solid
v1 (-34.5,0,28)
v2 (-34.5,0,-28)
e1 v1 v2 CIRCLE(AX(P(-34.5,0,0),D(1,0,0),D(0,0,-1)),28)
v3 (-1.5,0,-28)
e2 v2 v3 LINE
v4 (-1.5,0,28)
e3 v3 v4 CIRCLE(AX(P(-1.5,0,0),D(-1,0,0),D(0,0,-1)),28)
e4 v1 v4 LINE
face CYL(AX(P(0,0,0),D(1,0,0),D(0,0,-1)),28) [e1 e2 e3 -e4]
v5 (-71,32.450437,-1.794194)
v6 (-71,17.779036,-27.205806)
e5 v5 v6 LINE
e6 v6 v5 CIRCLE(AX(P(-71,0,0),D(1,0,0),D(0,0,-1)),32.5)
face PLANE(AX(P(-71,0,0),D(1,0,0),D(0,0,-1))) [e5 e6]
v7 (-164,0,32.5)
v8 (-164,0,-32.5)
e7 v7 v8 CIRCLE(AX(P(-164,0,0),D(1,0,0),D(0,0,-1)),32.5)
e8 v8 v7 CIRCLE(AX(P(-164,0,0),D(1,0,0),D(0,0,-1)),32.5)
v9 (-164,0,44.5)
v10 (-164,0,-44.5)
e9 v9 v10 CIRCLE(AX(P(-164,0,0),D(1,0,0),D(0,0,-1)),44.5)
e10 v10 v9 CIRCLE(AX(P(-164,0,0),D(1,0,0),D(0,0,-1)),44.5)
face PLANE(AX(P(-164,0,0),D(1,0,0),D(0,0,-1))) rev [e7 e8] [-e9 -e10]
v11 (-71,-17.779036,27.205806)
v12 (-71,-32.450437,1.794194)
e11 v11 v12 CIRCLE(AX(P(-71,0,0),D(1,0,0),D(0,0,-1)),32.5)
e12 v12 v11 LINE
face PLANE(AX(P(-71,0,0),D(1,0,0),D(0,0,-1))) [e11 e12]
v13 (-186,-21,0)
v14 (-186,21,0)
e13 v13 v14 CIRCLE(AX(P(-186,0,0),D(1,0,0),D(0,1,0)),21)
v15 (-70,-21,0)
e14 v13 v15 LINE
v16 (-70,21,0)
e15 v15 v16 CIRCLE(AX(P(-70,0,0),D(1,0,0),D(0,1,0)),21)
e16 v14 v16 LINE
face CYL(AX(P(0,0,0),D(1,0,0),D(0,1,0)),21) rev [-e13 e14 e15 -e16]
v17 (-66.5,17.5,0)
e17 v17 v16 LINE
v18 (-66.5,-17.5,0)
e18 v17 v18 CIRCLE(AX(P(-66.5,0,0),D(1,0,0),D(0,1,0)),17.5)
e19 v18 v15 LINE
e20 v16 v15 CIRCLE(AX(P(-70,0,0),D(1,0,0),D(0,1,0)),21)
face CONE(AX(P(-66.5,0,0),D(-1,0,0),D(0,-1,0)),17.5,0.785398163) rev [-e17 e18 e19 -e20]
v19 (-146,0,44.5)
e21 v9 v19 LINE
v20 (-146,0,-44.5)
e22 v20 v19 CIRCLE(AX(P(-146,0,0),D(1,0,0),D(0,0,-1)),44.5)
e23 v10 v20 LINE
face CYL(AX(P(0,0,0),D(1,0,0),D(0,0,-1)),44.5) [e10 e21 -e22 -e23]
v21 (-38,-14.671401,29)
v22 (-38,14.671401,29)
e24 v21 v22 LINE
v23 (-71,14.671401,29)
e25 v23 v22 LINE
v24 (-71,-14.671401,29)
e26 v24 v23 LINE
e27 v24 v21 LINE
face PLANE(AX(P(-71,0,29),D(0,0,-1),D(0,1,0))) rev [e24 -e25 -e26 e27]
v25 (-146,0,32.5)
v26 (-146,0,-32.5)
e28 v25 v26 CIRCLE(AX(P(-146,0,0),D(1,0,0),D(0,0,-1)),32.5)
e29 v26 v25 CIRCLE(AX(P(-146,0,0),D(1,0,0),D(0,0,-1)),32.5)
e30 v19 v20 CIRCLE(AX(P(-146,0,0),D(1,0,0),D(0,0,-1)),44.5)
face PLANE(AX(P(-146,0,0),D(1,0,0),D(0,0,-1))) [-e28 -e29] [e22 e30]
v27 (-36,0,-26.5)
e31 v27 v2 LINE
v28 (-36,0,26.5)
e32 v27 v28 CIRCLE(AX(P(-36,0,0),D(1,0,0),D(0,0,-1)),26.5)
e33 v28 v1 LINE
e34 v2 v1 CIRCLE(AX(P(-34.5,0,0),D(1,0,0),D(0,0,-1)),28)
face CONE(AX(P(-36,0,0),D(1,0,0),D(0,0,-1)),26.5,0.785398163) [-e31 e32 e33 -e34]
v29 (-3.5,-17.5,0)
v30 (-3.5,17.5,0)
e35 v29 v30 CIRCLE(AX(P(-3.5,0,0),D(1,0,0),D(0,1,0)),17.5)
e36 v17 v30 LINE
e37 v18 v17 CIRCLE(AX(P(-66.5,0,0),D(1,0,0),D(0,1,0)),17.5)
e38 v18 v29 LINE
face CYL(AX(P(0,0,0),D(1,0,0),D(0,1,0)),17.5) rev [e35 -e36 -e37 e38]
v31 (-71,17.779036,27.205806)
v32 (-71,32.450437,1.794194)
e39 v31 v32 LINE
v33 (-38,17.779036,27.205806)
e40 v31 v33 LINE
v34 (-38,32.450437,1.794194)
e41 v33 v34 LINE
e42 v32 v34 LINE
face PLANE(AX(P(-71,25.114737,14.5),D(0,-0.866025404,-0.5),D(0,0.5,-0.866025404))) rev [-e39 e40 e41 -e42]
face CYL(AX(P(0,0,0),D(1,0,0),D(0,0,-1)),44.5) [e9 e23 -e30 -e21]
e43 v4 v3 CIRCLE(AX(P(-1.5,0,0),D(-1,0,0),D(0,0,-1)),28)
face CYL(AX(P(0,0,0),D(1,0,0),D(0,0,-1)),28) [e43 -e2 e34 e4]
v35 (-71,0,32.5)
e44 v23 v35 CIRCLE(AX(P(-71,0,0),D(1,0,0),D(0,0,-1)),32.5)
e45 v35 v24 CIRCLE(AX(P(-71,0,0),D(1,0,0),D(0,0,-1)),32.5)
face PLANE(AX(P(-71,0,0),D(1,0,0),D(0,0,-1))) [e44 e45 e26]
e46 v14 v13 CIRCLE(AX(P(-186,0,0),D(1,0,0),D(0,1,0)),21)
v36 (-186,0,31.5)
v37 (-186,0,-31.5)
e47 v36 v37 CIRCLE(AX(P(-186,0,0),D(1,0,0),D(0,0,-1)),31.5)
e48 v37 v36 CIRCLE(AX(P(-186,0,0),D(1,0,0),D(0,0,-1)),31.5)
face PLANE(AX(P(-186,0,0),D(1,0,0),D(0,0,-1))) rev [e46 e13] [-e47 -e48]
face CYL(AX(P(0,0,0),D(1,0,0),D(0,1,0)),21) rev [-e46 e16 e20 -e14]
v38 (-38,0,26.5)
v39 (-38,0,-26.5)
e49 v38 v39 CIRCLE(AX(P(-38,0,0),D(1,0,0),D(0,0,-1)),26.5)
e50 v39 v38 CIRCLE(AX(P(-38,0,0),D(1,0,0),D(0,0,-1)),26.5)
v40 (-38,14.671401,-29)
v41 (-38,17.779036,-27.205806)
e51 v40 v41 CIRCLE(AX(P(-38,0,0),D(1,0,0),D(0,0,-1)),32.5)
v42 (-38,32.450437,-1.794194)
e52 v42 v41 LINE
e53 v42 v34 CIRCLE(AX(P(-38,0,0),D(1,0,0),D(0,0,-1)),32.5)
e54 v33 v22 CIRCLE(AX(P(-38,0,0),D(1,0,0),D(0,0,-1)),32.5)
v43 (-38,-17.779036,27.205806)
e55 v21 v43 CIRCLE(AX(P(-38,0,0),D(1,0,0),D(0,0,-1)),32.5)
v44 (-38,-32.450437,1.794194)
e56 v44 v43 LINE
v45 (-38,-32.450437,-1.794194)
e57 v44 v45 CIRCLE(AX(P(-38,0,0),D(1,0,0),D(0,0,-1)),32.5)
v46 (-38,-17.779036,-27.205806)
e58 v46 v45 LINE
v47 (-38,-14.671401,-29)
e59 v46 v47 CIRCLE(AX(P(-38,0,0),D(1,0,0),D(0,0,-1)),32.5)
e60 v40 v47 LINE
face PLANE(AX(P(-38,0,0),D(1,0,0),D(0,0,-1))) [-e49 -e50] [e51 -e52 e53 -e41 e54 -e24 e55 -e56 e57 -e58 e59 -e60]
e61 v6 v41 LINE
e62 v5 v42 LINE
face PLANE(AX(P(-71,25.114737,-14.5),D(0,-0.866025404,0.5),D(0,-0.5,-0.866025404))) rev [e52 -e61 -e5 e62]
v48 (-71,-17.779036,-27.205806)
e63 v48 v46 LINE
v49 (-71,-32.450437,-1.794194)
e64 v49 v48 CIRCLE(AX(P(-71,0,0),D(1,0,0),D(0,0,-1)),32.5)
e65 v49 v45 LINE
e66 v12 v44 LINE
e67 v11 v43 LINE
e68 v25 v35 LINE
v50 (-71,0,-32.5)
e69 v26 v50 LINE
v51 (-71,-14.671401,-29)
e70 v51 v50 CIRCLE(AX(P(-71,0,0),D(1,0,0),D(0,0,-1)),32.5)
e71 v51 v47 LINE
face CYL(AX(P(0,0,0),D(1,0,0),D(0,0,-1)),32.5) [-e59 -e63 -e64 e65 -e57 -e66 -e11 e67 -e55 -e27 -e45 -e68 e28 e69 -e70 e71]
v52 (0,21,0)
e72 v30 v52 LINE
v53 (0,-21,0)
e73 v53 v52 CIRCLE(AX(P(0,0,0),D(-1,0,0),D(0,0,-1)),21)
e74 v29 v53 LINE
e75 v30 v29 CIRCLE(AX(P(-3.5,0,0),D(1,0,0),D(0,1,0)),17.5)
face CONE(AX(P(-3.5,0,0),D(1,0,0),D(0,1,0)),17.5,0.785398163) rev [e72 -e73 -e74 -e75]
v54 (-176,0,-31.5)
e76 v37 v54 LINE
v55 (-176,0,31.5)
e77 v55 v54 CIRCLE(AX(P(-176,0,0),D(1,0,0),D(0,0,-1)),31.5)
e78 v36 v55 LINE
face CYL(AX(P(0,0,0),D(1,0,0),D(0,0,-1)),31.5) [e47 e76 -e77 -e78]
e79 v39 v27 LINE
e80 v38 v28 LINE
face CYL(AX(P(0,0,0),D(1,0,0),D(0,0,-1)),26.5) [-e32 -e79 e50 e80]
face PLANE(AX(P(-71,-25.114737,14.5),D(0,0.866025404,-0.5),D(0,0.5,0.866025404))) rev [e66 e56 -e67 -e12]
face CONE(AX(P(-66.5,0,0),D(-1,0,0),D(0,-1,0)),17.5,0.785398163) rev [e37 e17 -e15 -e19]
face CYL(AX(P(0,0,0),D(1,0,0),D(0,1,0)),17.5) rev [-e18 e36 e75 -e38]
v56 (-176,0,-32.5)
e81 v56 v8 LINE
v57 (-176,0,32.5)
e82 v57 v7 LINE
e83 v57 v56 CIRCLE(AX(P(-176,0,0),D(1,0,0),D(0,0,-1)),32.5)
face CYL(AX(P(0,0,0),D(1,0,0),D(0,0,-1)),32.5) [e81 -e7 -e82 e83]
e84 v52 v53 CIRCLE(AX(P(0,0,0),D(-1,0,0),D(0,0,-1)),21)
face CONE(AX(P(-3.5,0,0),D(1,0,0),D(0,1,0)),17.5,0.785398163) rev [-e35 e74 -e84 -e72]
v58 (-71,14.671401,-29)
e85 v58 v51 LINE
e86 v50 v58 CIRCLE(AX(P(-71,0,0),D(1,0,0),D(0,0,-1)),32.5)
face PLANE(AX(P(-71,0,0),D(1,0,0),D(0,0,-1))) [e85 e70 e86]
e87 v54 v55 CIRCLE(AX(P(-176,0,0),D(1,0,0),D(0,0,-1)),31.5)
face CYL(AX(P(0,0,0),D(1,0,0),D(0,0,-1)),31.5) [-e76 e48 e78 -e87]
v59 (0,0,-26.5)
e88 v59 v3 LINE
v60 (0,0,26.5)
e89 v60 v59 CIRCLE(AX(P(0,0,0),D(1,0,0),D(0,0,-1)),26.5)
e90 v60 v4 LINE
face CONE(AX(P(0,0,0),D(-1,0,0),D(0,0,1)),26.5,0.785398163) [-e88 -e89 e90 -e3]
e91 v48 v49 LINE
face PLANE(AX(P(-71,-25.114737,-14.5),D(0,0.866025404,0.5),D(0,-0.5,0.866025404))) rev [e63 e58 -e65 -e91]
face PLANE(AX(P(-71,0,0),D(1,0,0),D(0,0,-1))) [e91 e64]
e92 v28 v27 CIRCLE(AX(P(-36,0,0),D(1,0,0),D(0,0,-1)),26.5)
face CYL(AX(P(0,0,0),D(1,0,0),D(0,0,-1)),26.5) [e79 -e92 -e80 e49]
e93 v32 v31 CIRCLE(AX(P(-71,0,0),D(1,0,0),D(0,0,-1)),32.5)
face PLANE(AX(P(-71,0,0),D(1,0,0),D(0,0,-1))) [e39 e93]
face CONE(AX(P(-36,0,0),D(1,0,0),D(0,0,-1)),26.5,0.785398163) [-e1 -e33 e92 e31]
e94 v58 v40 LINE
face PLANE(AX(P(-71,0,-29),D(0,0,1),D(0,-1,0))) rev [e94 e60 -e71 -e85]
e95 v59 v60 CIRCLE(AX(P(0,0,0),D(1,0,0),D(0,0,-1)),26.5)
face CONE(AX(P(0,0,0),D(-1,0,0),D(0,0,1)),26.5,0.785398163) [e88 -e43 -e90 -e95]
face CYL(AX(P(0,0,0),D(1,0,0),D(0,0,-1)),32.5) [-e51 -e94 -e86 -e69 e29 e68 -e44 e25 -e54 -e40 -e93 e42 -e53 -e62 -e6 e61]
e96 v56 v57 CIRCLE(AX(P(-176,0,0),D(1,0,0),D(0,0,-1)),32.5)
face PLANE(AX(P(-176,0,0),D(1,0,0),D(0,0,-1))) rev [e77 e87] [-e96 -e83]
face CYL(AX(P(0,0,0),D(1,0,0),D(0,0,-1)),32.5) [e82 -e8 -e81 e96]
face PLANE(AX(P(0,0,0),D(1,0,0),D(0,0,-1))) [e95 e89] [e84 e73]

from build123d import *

# Parameters (mm, degrees)
CHAMFER1_SIZE      = 1.5
CUT_EXTRUDE1_START = -33
CUT_EXTRUDE1_DEPTH = 71
CIRPATTERN1_COUNT  = 6
CHAMFER3_SIZE      = 3.5


with BuildPart() as part:
    # Sketch1 → Revolve1 (revolve)
    with BuildSketch(Plane.XY, mode=Mode.PRIVATE) as revolve1_sk:
        Polygon((-34.5, 28), (-36, 26.5), (-38, 26.5), (-38, 28), (-38, 32.5), (-146, 32.5), (-146, 44.5), (-164, 44.5), (-164, 32.5), (-176, 32.5), (-176, 31.5), (-186, 31.5), (-186, 0), (-176, 0), (-164, 0), (-146, 0), (-38, 0), (0, 0), (0, 28), align=None)
    revolve(revolve1_sk.sketch.rotate(Axis((0, 0, 0), (-1, 0, 0)), 90), axis=Axis((0, 0, 0), (-1, 0, 0)))

    # Chamfer1
    chamfer1_edges = [part.edges().sort_by_distance(p)[0] for p in [
        (0, 0, 28),
    ]]
    chamfer(chamfer1_edges, length=CHAMFER1_SIZE)

    # Sketch2 → Cut-Extrude1 (cut)
    with BuildSketch(Plane(origin=(-38, 0, 0), x_dir=(0, 0, -1), z_dir=(1, 0, 0)).offset(CUT_EXTRUDE1_START)):
        with BuildLine():
            Line((1.79419424, 32.450437085), (27.20580576, 17.779036334))
            ThreePointArc((27.20580576, 17.779036334), (16.25, 28.145825623), (1.79419424, 32.450437085))
        make_face()
    cut_extrude1 = extrude(amount=CUT_EXTRUDE1_DEPTH, mode=Mode.SUBTRACT)

    # CirPattern1: Cut-Extrude1 ×6 about axis
    cirpattern1_axis = Axis((0, 0, 0), (1, 0, 0))
    for i in range(1, CIRPATTERN1_COUNT):
        add(cut_extrude1.rotate(cirpattern1_axis, i * 360 / CIRPATTERN1_COUNT), mode=Mode.SUBTRACT)

    # Sketch4 → Cut-Revolve2 (revolve, cut)
    with BuildSketch(Plane.XY):
        Polygon((0, 0), (-70, 0), (-186, 0), (-186, 21), (-70, 21), (-66.5, 17.5), (0, 17.5), align=None)
    revolve(axis=Axis((0, 0, 0), (-1, 0, 0)), mode=Mode.SUBTRACT)

    # Chamfer3
    chamfer3_edges = [part.edges().sort_by_distance(p)[0] for p in [
        (0, -17.5, 0),
    ]]
    chamfer(chamfer3_edges, length=CHAMFER3_SIZE)


solid = part.part
